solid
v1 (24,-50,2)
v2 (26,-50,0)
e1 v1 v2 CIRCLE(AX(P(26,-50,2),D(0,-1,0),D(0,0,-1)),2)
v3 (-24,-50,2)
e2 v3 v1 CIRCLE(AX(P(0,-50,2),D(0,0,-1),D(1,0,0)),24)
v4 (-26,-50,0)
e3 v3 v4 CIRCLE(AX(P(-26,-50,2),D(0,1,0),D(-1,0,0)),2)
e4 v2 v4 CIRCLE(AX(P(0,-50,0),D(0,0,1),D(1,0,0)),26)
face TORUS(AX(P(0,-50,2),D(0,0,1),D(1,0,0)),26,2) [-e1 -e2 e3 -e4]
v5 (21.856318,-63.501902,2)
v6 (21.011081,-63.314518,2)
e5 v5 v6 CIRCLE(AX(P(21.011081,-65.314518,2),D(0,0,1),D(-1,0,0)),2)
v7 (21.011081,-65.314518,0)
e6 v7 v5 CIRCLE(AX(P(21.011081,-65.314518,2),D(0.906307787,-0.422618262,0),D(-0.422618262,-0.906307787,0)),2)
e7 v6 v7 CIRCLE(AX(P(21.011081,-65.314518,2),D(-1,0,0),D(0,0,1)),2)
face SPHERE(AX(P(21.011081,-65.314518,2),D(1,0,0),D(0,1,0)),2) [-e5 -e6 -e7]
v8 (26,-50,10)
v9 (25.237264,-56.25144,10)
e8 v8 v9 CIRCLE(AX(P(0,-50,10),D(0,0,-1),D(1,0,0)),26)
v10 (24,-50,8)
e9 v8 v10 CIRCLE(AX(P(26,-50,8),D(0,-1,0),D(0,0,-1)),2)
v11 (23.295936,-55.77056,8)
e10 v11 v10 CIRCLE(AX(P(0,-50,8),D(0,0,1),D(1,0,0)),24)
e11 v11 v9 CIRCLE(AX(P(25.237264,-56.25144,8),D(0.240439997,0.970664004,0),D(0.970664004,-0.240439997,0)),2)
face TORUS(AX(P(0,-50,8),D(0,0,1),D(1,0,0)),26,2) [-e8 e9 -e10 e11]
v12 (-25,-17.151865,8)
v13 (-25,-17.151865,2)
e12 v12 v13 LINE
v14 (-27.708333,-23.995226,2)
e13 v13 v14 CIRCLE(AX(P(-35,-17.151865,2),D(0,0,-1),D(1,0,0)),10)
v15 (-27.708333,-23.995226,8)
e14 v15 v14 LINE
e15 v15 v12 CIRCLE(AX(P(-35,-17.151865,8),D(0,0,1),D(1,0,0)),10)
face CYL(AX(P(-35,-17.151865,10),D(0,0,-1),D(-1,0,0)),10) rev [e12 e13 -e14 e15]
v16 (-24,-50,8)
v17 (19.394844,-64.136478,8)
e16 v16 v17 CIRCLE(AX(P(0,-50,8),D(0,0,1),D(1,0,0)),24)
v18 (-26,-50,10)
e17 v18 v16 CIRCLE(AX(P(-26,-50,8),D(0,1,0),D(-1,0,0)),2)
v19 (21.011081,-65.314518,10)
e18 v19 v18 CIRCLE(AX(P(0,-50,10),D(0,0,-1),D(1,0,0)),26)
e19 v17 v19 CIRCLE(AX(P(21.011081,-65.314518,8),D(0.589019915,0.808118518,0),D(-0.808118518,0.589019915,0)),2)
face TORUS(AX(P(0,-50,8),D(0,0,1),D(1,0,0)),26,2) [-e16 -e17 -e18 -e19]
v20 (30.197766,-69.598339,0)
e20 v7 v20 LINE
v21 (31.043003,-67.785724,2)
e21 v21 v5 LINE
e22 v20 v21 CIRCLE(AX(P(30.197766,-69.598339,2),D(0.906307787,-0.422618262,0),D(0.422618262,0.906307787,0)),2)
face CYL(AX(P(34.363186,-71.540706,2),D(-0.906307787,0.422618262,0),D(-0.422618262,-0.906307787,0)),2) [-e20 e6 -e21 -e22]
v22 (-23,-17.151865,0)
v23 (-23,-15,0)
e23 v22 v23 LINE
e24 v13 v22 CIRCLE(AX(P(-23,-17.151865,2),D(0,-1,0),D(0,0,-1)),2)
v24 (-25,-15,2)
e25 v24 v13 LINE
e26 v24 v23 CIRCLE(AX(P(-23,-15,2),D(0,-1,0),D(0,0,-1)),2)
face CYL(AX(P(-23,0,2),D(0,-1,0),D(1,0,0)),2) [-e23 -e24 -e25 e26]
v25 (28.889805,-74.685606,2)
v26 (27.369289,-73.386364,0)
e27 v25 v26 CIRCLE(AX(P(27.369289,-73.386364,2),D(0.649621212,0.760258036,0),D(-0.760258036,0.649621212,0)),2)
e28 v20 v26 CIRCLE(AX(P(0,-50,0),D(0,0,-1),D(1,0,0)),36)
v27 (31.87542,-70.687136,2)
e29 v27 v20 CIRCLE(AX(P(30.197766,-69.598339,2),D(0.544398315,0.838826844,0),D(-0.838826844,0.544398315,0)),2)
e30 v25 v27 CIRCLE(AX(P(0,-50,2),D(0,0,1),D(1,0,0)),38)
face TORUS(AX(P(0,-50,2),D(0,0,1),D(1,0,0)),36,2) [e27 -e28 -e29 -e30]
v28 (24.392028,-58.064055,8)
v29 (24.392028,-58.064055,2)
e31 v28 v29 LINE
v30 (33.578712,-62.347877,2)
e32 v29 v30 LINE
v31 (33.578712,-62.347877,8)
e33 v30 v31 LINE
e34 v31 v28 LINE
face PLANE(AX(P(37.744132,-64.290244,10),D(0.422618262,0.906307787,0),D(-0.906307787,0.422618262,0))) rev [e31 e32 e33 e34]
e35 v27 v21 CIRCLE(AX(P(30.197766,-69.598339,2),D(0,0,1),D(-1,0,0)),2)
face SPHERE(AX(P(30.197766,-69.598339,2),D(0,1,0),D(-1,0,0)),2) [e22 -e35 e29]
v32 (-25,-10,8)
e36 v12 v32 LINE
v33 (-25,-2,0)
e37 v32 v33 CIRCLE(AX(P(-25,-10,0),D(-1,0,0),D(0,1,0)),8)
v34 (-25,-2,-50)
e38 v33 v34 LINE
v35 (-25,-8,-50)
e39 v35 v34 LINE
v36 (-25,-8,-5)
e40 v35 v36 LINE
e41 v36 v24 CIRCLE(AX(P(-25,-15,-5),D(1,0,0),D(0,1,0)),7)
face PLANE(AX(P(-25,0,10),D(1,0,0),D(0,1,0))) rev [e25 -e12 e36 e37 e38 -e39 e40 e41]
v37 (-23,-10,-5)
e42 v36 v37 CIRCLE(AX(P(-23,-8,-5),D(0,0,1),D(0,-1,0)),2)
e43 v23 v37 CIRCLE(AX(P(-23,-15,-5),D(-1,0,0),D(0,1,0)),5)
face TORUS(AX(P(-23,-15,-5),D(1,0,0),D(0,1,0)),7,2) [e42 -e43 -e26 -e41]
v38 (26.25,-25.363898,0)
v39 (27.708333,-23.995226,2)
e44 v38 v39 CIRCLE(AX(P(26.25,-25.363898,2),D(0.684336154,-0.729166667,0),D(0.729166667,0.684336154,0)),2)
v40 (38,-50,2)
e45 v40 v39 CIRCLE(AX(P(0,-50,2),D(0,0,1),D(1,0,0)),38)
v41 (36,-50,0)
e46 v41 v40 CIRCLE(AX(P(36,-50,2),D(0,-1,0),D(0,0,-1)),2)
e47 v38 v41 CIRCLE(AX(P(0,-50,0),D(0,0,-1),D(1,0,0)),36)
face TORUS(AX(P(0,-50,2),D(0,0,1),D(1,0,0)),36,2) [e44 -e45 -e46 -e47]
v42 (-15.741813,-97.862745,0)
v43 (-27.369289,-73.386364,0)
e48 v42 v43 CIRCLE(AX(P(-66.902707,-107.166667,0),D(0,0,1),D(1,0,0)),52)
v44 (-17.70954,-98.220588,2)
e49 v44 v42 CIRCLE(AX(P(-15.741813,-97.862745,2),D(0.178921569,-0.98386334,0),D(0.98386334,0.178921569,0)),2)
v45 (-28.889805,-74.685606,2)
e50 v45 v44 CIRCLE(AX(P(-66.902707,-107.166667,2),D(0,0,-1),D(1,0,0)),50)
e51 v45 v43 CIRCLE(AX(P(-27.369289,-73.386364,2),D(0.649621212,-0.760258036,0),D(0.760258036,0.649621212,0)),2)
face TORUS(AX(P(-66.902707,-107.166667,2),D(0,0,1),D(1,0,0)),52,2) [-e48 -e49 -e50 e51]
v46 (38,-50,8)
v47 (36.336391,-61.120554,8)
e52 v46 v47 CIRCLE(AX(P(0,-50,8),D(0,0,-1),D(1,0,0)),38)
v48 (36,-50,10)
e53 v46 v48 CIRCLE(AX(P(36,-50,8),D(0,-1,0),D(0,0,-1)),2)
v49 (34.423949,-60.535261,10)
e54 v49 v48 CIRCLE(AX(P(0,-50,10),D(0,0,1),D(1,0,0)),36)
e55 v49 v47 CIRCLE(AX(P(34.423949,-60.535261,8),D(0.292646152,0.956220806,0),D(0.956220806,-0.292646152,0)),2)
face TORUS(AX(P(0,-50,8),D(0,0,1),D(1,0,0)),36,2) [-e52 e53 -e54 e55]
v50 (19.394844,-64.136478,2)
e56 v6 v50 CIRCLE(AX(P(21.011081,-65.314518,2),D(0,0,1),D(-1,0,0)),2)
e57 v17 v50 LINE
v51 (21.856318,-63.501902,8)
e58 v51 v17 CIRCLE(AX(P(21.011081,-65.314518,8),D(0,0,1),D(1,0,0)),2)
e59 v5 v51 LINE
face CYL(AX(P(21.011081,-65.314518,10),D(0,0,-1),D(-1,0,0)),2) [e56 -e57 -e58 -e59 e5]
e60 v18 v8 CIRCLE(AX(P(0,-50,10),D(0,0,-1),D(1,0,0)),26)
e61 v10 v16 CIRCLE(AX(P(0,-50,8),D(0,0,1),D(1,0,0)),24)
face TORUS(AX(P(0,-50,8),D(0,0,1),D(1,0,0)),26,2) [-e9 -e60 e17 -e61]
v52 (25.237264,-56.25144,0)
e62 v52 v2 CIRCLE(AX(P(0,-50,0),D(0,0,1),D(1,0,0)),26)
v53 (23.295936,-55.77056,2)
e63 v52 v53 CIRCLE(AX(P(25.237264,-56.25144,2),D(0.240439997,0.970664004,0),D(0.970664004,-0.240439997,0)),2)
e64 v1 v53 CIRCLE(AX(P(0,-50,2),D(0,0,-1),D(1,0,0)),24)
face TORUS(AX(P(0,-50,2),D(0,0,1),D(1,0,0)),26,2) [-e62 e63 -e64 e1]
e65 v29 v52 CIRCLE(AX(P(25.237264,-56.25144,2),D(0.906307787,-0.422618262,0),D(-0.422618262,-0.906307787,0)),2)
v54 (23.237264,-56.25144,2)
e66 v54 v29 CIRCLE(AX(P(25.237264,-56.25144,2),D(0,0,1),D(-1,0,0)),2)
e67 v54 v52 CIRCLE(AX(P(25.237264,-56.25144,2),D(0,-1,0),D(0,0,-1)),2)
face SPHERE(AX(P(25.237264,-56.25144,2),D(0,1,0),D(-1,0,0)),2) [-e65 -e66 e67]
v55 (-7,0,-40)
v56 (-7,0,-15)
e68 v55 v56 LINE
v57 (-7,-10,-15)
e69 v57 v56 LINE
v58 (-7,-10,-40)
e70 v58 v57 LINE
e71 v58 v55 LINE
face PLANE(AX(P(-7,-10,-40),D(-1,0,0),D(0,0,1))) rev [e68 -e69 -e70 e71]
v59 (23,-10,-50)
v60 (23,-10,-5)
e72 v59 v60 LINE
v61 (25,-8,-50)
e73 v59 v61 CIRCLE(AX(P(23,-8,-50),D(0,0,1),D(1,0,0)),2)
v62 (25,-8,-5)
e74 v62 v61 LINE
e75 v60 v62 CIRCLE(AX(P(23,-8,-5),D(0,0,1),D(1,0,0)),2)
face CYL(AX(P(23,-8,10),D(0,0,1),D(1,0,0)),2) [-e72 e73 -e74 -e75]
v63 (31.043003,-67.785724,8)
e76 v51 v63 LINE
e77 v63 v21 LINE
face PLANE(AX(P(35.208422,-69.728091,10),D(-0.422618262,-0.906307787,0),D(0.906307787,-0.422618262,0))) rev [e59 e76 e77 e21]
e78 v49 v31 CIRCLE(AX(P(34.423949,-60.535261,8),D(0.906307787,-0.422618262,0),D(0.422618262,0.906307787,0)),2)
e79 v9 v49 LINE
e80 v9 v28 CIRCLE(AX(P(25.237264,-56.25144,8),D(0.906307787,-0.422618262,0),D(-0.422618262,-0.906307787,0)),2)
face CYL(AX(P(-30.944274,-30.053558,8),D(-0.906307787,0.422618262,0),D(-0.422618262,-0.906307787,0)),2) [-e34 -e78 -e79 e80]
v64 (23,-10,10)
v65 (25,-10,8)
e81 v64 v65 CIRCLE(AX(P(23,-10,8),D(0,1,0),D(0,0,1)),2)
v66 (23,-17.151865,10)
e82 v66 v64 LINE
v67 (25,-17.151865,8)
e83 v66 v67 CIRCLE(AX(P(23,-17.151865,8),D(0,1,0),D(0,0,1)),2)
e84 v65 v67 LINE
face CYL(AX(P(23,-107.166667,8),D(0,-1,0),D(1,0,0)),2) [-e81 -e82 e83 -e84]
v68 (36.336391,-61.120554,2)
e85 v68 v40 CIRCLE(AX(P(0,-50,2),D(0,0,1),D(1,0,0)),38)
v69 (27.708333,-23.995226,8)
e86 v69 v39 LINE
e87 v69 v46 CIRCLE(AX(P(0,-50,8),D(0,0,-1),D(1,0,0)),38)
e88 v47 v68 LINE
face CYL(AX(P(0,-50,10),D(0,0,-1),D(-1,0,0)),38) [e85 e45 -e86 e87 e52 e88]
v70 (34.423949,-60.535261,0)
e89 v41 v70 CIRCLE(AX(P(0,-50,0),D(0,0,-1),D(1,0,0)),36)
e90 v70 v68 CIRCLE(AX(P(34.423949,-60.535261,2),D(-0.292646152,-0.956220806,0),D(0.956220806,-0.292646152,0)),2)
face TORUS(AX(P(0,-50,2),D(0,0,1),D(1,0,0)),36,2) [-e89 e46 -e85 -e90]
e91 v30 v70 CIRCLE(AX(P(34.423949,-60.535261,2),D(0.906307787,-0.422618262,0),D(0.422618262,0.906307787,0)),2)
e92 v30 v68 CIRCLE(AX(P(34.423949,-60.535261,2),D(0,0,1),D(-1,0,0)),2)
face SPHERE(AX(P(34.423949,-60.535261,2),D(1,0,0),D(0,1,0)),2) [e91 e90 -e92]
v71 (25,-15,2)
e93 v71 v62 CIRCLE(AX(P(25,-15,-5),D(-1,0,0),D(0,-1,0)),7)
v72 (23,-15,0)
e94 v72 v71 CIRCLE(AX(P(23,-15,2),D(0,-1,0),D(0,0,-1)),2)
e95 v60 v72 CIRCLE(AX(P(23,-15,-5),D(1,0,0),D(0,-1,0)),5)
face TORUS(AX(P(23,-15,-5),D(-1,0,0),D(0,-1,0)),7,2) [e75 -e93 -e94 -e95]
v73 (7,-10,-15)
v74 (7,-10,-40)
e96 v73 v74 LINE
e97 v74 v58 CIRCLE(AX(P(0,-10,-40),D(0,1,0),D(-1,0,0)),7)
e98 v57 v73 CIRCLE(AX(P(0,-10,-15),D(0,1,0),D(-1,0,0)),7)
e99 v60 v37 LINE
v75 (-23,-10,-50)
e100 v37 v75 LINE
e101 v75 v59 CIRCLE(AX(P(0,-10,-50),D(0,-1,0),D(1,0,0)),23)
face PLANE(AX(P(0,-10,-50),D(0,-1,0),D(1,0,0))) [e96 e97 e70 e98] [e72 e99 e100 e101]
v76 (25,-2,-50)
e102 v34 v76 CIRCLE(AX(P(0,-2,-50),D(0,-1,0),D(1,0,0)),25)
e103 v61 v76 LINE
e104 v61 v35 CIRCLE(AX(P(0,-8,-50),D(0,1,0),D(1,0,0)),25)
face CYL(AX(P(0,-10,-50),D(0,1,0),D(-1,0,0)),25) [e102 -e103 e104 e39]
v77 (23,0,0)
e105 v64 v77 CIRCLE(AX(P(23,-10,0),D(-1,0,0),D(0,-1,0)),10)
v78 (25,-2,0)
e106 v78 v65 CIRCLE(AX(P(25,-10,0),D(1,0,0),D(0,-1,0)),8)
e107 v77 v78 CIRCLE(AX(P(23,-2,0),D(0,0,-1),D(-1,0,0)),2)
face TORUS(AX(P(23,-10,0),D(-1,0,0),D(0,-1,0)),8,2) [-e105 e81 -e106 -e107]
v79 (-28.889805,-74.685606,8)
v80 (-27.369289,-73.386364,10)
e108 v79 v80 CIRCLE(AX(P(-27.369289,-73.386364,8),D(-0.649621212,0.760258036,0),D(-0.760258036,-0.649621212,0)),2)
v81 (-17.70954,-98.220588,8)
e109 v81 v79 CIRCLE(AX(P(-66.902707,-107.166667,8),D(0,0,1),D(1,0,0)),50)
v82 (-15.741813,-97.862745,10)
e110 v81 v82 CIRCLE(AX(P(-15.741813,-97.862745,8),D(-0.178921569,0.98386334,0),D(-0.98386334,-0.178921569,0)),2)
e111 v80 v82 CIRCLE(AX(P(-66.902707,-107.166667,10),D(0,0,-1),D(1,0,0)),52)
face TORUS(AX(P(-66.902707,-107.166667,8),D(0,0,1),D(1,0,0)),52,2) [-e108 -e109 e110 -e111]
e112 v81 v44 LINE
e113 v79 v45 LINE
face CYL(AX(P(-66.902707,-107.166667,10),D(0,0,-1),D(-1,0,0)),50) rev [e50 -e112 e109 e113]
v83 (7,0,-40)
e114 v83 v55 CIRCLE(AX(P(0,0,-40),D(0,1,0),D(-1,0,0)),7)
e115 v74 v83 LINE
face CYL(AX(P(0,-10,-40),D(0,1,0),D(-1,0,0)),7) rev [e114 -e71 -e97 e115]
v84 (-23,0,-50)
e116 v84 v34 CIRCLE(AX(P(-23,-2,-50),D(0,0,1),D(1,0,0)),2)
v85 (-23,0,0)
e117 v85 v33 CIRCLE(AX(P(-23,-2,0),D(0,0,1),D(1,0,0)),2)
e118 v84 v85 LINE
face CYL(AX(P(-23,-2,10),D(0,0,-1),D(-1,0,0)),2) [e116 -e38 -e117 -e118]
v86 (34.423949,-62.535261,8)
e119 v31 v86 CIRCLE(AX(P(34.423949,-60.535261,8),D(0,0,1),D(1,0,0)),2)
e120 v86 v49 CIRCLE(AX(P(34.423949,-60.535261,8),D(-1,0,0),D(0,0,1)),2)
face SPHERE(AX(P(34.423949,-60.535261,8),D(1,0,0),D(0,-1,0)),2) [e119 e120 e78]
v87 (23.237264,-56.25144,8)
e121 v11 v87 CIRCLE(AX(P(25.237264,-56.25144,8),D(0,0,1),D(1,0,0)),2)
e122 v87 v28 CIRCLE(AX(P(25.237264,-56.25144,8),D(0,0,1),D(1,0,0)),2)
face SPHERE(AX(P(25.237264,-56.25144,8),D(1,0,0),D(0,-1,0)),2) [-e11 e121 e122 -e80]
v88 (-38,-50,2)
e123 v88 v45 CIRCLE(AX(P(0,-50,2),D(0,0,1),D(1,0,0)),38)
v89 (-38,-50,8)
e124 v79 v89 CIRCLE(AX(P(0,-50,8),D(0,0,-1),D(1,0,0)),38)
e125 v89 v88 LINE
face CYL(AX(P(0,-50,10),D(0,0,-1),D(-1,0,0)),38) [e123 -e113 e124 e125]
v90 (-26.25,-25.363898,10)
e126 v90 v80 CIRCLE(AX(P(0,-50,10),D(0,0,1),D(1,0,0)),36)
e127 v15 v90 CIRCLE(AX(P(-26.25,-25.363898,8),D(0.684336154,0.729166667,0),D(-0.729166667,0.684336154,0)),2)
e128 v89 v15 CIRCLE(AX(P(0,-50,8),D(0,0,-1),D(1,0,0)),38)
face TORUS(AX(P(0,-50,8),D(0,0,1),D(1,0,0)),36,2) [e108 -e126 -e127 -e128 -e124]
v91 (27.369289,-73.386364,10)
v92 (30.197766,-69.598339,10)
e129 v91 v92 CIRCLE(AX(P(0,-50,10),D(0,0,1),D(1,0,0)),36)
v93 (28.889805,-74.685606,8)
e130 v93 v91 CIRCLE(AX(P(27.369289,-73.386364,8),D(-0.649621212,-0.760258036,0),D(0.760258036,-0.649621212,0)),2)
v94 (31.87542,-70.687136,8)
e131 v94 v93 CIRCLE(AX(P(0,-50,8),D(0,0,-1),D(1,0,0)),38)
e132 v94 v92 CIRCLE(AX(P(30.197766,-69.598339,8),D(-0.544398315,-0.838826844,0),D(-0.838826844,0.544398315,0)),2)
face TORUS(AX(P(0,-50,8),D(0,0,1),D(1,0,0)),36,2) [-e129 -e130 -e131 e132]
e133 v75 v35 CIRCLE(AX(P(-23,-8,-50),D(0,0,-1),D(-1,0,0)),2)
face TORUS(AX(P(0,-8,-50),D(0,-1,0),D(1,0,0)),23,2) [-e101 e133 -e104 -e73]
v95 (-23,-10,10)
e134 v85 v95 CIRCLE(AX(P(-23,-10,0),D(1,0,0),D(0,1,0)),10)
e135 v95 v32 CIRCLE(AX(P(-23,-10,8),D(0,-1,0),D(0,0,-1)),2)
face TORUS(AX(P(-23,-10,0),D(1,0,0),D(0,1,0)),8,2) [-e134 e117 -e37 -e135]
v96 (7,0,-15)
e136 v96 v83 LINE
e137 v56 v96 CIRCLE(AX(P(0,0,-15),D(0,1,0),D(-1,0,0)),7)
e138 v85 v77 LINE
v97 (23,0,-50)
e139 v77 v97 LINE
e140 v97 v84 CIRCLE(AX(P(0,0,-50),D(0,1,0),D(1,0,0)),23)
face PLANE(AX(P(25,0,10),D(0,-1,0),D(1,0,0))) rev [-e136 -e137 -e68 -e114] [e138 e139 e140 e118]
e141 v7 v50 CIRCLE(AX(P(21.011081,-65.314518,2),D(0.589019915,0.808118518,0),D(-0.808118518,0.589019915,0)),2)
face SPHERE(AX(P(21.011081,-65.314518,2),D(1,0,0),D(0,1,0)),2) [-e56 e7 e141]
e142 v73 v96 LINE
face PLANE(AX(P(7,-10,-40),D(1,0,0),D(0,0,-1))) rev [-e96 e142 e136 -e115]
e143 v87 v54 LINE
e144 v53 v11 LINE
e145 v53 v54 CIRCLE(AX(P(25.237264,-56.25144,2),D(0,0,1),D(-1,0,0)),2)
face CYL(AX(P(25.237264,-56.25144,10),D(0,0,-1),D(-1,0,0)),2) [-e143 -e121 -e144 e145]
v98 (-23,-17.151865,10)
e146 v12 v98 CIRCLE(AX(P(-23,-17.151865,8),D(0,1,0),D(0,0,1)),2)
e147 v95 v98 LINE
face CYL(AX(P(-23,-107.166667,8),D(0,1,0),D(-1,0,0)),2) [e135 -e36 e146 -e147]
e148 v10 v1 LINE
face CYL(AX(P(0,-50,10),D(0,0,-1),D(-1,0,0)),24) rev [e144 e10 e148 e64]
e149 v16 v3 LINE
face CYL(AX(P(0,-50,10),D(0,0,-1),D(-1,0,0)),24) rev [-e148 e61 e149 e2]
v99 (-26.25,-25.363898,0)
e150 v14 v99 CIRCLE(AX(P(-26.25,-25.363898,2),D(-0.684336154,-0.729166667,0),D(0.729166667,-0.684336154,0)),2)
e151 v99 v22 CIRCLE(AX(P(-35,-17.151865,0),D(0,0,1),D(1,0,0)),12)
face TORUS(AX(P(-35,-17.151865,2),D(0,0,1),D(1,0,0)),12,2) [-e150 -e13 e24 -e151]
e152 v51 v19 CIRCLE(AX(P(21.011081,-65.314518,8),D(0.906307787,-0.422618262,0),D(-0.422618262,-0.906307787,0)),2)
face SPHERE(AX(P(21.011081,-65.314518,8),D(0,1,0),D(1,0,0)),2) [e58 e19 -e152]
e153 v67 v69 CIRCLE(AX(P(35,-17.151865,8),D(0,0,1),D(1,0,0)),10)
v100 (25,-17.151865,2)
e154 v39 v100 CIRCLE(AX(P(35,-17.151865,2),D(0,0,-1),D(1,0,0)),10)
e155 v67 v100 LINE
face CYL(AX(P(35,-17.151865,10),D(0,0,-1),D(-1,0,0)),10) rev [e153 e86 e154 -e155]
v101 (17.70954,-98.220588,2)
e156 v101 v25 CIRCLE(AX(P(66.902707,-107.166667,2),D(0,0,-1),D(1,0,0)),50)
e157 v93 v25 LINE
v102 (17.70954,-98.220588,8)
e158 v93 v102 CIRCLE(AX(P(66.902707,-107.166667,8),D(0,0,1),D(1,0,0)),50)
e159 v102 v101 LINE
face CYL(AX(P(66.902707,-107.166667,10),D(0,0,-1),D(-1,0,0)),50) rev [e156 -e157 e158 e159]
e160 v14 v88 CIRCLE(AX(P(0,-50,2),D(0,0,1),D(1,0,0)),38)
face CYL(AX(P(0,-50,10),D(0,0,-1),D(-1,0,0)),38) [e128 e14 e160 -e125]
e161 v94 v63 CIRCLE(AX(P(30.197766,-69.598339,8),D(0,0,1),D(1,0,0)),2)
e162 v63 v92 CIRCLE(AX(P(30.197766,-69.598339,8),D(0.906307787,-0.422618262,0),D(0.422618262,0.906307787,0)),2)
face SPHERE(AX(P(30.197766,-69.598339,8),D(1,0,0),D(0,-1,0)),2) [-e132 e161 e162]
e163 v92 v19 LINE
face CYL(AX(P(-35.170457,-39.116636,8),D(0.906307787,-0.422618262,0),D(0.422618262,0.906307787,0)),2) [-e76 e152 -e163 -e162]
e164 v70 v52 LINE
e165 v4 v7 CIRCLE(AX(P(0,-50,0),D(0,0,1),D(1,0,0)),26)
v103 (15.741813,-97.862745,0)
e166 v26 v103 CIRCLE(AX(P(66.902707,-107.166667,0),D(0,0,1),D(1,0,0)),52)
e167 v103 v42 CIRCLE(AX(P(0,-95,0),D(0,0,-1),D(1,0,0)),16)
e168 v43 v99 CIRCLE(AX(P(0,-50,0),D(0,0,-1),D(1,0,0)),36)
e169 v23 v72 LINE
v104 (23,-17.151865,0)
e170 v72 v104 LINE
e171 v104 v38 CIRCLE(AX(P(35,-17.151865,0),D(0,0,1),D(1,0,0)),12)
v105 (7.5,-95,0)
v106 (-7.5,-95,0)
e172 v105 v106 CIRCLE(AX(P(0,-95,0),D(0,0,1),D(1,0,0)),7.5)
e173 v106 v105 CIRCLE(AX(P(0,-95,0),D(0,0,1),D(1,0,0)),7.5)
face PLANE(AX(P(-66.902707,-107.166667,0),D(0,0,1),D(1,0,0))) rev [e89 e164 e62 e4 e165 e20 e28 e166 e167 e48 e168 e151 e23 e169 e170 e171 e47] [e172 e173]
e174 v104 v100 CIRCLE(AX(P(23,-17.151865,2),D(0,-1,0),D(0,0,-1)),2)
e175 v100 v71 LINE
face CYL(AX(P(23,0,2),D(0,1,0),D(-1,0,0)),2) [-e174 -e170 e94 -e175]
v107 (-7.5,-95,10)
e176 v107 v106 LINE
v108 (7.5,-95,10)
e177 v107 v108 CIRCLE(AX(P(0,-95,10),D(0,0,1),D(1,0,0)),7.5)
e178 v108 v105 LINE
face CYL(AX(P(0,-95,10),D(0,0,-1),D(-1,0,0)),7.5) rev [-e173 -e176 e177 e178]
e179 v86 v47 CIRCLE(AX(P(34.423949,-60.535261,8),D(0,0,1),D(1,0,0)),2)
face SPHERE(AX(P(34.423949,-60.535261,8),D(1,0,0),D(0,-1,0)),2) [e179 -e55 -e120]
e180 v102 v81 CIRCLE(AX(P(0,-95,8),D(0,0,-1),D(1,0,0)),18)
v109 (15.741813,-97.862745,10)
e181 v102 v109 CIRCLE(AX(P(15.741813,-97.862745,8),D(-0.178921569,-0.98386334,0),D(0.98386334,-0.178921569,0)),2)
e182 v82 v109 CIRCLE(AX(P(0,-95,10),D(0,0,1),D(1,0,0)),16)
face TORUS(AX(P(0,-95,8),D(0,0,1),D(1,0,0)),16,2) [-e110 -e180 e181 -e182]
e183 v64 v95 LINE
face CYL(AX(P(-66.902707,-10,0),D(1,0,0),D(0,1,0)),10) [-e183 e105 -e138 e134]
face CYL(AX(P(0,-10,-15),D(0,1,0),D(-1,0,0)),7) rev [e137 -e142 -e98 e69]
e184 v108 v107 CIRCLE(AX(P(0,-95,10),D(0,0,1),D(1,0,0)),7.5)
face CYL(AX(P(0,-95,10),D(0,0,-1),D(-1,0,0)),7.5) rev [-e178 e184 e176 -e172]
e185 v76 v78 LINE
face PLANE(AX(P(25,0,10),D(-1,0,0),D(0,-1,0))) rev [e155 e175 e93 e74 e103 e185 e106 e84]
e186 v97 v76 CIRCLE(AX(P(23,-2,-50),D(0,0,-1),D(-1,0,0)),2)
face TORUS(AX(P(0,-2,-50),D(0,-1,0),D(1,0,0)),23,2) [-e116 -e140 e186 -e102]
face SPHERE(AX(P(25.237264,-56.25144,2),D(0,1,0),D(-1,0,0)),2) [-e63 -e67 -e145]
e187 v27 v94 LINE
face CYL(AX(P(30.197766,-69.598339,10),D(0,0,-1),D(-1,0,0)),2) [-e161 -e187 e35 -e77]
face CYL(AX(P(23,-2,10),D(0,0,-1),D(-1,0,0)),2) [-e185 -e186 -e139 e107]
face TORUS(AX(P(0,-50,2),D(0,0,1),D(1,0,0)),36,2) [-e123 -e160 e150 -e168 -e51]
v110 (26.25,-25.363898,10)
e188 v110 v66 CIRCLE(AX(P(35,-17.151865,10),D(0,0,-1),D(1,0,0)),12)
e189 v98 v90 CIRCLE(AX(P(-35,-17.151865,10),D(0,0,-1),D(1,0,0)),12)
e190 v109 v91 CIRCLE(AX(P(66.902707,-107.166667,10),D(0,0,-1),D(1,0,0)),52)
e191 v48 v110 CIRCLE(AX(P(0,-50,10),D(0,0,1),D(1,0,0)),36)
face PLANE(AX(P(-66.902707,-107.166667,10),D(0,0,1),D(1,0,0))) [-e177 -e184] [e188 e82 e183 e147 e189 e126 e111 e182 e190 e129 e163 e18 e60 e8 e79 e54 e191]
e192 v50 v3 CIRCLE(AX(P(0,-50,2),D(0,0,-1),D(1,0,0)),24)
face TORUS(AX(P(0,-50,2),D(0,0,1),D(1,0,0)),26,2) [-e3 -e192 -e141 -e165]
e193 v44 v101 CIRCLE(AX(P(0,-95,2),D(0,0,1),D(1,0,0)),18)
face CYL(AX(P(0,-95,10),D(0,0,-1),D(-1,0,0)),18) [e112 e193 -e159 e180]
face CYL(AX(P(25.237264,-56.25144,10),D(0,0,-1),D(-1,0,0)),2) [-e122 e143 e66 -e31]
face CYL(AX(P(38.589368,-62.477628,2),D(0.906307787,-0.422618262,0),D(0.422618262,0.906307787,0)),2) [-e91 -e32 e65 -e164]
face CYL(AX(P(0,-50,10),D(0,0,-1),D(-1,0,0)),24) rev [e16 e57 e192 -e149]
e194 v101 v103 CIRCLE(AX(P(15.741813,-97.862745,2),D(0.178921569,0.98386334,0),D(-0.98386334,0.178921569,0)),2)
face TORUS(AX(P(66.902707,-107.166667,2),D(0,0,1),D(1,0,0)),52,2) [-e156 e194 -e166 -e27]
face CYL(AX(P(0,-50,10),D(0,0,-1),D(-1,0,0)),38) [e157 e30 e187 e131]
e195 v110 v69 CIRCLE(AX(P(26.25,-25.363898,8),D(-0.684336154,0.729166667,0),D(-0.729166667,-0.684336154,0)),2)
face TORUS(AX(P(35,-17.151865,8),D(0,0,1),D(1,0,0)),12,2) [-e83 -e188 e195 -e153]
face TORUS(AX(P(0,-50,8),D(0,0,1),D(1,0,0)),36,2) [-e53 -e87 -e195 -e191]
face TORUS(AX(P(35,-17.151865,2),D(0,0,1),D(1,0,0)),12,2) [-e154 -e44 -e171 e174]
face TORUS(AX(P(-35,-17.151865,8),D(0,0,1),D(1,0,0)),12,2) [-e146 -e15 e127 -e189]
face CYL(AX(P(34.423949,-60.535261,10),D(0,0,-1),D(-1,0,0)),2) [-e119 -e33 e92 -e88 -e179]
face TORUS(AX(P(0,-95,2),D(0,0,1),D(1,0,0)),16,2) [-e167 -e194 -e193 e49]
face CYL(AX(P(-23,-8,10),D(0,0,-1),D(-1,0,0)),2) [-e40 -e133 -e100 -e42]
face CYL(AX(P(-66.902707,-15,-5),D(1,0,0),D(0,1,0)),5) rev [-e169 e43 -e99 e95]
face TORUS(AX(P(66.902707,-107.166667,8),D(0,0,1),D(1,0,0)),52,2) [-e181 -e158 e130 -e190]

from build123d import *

# Parameters (mm, degrees)
CLAMP_PLATE_SKETCH_R      = 24
CLAMP_PLATE_SKETCH_R_2    = 7.5
CLAMP_RING_PLATE_DEPTH    = 10
SLOTTED_TOP_FLANGE_DEPTH  = 10
CLAMP_SPLIT_CUT_DEPTH     = 141.847435191
FLANGE_BEND_FILLET_R5_R   = 5
PLATE_CORNER_FILLET_R10_R = 10
EDGE_BREAK_FILLETS_R2_R   = 2


with BuildPart() as part:
    # Clamp Plate Sketch → Clamp Ring Plate (new body)
    with BuildSketch(Plane.XY):
        with BuildLine():
            Line((25, 0), (25, -17.151864589))
            ThreePointArc((25, -17.151864589), (25.701702665, -20.83176495), (27.708333333, -23.995226133))
            ThreePointArc((27.708333333, -23.995226133), (37.989682547, -49.114550984), (28.889805354, -74.685606061))
            ThreePointArc((28.889805354, -74.685606061), (21.739686255, -85.712027428), (17.709540124, -98.220588235))
            ThreePointArc((17.709540124, -98.220588235), (0, -113), (-17.709540124, -98.220588235))
            ThreePointArc((-17.709540124, -98.220588235), (-21.739686255, -85.712027428), (-28.889805354, -74.685606061))
            ThreePointArc((-28.889805354, -74.685606061), (-37.989682547, -49.114550984), (-27.708333333, -23.995226133))
            ThreePointArc((-27.708333333, -23.995226133), (-25.701702665, -20.83176495), (-25, -17.151864589))
            Line((-25, -17.151864589), (-25, 0))
            Line((-25, 0), (25, 0))
        make_face()
        with Locations((0, -50)):
            Circle(CLAMP_PLATE_SKETCH_R, mode=Mode.SUBTRACT)
        with Locations((0, -95)):
            Circle(CLAMP_PLATE_SKETCH_R_2, mode=Mode.SUBTRACT)
    extrude(amount=CLAMP_RING_PLATE_DEPTH)

    # Top Flange Sketch → Slotted Top Flange (add)
    with BuildSketch(Plane(origin=(0, 0, 0), x_dir=(1, 0, 0), z_dir=(0, 1, 0))):
        with BuildLine():
            Line((-25, -10), (25, -10))
            Line((25, -10), (25, 50))
            ThreePointArc((25, 50), (0, 75), (-25, 50))
            Line((-25, 50), (-25, -10))
        make_face()
        with BuildLine():
            Line((7, 40), (7, 15))
            ThreePointArc((7, 15), (0, 8), (-7, 15))
            Line((-7, 15), (-7, 40))
            ThreePointArc((-7, 40), (0, 47), (7, 40))
        make_face(mode=Mode.SUBTRACT)
    extrude(amount=-SLOTTED_TOP_FLANGE_DEPTH)

    # Clamp Split Sketch → Clamp Split Cut (cut, through all)
    with BuildSketch(Plane(origin=(0, 0, 0), x_dir=(-1, 0, 0), z_dir=(0, 0, -1))):
        Polygon((-37.744131876, -64.290243987), (-18.548040224, -55.338959443), (-16.012330654, -60.776806166), (-35.208422306, -69.72809071), align=None)
    extrude(amount=-CLAMP_SPLIT_CUT_DEPTH, mode=Mode.SUBTRACT)

    # Flange Bend Fillet R5
    flange_bend_fillet_r5_edges = [part.edges().sort_by_distance(p)[0] for p in [
        (0, -10, 0),
    ]]
    fillet(flange_bend_fillet_r5_edges, radius=FLANGE_BEND_FILLET_R5_R)

    # Plate Corner Fillet R10
    plate_corner_fillet_r10_edges = [part.edges().sort_by_distance(p)[0] for p in [
        (0, 0, 10),
    ]]
    fillet(plate_corner_fillet_r10_edges, radius=PLATE_CORNER_FILLET_R10_R)

    # Edge Break Fillets R2
    edge_break_fillets_r2_edges = [part.edges().sort_by_distance(p)[0] for p in [
        (-25, -16.075932294, 0),
        (25, -10, -27.5),
        (25, -11.464466094, -1.464466094),
        (-37.989682547, -49.114550984, 0),
        (-25, -11.464466094, -1.464466094),
        (-25.701702665, -20.83176495, 0),
        (-25, -13.575932294, 10),
        (-25, 0, -25),
        (-25, -2.928932188, 7.071067812),
        (25, 0, -25),
        (25, -2.928932188, 7.071067812),
        (25, -16.075932294, 0),
        (25.701702665, -20.83176495, 0),
        (31.119955968, -71.807070885, 0),
        (21.739686255, -85.712027428, 10),
        (21.739686255, -85.712027428, 0),
        (0, -113, 0),
        (-21.739686255, -85.712027428, 0),
        (31.119955968, -71.807070885, 10),
        (25.701702665, -20.83176495, 10),
        (25, -13.575932294, 10),
        (-25.701702665, -20.83176495, 10),
        (-37.989682547, -49.114550984, 10),
        (-25, -10, -27.5),
        (0, 0, -75),
        (0, -10, -75),
        (-21.739686255, -85.712027428, 10),
        (-21.751386889, -39.857161718, 10),
        (-21.751386889, -39.857161718, 0),
        (20.312930357, -62.782208742, 5),
        (22.848639927, -57.34436202, 5),
        (37.256095308, -42.517796957, 0),
        (37.256095308, -42.517796957, 10),
        (29.224348471, -60.31740374, 10),
        (35.600057015, -63.29044546, 5),
        (33.064347445, -68.728292182, 5),
        (26.688638901, -65.755250462, 10),
        (26.688638901, -65.755250462, 0),
        (29.224348471, -60.31740374, 0),
        (0, -113, 10),
    ]]
    fillet(edge_break_fillets_r2_edges, radius=EDGE_BREAK_FILLETS_R2_R)


solid = part.part
